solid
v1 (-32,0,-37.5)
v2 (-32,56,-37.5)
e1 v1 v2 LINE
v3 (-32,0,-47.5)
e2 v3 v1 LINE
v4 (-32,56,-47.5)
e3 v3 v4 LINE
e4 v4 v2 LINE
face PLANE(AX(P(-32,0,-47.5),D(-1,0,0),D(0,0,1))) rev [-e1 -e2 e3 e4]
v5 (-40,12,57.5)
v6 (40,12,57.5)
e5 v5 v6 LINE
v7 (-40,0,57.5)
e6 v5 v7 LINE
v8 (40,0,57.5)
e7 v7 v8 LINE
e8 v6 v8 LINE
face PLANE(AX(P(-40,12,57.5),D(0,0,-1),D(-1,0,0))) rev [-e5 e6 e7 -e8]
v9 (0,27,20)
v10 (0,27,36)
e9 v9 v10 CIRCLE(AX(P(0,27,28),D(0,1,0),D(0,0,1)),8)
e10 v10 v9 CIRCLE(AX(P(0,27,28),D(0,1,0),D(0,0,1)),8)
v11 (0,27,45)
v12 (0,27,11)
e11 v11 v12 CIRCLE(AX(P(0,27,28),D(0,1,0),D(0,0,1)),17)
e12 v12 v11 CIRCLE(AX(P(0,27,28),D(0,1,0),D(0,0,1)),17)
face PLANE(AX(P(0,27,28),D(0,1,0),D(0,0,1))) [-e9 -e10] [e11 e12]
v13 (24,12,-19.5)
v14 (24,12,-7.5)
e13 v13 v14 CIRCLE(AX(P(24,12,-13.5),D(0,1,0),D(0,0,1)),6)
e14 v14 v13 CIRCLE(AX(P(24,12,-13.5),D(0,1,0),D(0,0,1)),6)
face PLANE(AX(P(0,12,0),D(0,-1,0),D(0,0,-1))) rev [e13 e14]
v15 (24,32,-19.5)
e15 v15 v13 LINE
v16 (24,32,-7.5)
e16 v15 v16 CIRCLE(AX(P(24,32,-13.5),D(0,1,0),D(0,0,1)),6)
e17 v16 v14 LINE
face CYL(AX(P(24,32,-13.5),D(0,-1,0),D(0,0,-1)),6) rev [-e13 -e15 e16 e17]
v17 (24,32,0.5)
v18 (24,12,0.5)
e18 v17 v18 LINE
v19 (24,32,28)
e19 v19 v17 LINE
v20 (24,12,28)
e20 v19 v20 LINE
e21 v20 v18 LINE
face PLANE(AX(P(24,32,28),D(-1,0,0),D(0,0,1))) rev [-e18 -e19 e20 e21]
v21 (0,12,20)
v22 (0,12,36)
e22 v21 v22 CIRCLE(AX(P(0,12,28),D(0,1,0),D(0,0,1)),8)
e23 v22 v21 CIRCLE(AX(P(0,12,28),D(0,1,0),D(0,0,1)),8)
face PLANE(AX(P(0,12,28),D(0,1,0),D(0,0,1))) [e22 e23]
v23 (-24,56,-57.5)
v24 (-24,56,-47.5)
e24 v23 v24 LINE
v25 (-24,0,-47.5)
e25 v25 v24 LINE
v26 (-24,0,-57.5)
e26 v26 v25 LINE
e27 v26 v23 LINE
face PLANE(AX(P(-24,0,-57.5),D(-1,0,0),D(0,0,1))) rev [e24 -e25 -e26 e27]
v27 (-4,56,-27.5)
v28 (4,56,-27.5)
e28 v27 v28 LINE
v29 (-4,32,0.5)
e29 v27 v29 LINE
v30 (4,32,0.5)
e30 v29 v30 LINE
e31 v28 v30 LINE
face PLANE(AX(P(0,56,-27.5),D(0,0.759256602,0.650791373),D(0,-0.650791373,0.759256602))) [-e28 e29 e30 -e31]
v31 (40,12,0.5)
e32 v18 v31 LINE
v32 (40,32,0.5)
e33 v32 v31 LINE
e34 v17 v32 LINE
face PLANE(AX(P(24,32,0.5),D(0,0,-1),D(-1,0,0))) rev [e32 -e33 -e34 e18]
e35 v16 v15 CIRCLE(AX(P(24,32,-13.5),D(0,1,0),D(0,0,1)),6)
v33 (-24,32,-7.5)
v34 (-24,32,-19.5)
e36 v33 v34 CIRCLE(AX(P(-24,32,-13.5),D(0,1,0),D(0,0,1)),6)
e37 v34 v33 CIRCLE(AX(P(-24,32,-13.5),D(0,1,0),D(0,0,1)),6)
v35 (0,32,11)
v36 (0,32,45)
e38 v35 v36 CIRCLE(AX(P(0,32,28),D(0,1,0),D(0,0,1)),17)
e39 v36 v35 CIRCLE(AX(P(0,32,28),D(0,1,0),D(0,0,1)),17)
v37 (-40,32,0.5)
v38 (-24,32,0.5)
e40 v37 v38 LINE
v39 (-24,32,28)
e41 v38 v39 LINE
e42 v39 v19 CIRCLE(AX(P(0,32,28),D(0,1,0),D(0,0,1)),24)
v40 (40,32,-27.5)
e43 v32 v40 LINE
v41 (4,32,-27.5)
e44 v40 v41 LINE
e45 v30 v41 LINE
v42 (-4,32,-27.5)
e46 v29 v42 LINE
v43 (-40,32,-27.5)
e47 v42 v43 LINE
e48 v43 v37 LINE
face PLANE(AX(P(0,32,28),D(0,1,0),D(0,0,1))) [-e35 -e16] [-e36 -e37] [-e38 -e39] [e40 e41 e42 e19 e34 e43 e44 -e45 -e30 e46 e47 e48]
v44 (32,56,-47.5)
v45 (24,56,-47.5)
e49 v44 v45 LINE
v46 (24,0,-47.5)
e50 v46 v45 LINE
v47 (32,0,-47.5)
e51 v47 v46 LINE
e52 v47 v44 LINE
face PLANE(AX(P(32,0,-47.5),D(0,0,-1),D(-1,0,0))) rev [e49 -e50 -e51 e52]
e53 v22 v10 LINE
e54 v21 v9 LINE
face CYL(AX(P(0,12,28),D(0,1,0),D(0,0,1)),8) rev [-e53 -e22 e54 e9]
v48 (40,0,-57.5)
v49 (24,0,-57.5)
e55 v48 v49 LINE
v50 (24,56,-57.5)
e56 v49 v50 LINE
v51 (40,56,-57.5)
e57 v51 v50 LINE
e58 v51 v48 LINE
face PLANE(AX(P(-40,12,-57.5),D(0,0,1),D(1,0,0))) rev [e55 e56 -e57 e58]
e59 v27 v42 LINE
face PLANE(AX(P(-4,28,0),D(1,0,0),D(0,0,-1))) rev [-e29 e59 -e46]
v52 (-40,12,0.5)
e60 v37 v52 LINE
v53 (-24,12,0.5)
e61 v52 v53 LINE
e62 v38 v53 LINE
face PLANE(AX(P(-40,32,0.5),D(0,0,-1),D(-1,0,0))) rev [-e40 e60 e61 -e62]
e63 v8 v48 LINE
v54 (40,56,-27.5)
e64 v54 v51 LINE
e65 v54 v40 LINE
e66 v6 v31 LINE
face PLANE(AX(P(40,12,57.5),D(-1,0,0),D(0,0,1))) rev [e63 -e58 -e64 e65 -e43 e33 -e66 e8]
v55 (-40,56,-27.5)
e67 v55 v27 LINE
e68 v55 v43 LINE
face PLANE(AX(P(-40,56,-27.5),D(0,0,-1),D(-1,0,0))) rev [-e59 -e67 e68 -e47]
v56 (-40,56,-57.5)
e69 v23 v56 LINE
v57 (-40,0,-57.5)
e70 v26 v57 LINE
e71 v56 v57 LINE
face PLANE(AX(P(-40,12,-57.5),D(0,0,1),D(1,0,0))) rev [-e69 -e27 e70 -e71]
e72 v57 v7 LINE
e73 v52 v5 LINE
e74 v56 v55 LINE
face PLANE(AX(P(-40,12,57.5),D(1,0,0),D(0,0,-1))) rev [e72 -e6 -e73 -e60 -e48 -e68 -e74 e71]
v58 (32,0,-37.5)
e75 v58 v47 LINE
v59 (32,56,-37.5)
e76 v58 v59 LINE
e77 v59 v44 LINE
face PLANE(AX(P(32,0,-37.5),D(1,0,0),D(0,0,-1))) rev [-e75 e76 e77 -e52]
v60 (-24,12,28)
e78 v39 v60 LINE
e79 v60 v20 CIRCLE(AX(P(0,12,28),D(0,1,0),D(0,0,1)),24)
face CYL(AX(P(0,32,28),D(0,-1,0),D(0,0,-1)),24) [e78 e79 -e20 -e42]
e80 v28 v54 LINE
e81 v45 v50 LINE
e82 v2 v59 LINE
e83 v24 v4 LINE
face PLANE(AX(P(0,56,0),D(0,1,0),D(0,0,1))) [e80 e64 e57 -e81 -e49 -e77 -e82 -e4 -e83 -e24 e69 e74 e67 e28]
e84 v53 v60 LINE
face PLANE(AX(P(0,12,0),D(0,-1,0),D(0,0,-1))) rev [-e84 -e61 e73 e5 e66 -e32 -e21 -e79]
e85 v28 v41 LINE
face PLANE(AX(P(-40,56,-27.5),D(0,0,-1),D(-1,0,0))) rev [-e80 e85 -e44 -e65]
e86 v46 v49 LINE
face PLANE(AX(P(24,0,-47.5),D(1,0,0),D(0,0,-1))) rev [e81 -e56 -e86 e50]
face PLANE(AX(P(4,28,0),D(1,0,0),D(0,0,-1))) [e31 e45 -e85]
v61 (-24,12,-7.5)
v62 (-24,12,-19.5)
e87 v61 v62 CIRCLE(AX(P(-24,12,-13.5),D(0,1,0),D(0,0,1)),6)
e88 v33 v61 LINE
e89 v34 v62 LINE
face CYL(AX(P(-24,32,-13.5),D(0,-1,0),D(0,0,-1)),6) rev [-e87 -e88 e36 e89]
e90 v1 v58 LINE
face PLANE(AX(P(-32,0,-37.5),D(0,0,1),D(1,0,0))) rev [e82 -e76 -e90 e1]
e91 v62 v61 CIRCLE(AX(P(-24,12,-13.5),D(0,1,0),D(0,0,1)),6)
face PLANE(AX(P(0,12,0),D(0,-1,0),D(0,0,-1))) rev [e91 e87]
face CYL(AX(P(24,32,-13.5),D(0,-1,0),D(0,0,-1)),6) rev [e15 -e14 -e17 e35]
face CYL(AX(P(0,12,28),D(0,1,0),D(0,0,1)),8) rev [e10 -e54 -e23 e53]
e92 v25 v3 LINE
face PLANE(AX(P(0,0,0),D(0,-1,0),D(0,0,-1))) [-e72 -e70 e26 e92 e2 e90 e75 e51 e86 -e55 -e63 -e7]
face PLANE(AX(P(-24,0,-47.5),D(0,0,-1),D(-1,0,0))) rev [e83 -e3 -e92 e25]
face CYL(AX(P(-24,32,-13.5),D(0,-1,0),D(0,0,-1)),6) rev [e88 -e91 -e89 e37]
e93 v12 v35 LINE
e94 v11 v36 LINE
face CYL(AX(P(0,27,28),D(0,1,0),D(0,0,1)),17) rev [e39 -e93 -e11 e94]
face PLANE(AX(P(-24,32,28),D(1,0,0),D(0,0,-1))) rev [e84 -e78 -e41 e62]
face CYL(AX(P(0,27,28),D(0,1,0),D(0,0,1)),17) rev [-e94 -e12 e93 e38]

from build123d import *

# Parameters (mm, degrees)
BASE_PLATE_SKETCH_W    = 80
BASE_PLATE_SKETCH_H    = 115
BASE_PLATE_DEPTH       = 12
BACK_WALL_SKETCH_W     = 80
BACK_WALL_SKETCH_H     = 30
BACK_WALL_DEPTH        = 44
WALL_SLOT_CUT_DEPTH    = 90.678592763
BOSS_PAD_SKETCH_R      = 6
BOSS_PAD_DEPTH         = 20
COUNTERBORE_SKETCH_R   = 17
COUNTERBORE_34X5_DEPTH = 5
BORE_SKETCH_R          = 8
BORE_16_DEPTH          = 15
SUPPORT_RIB_8MM_REACH  = 91.679
RIB_SKETCH_WALL_W      = 218.235363356
RIB_SKETCH_WALL_H      = 8


with BuildPart() as part:
    # Base Plate Sketch → Base Plate (new body)
    with BuildSketch(Plane(origin=(0, 0, 0), x_dir=(1, 0, 0), z_dir=(0, 1, 0))):
        Rectangle(BASE_PLATE_SKETCH_W, BASE_PLATE_SKETCH_H)
    extrude(amount=BASE_PLATE_DEPTH)

    # Back Wall Sketch → Back Wall (add)
    with BuildSketch(Plane(origin=(0, 12, 0), x_dir=(1, 0, 0), z_dir=(0, 1, 0))):
        with Locations((0, 42.5)):
            Rectangle(BACK_WALL_SKETCH_W, BACK_WALL_SKETCH_H)
    extrude(amount=BACK_WALL_DEPTH)

    # Wall Slot Sketch → Wall Slot Cut (cut, through all)
    with BuildSketch(Plane(origin=(0, 56, 0), x_dir=(1, 0, 0), z_dir=(0, 1, 0))):
        Polygon((-24, 57.5), (-24, 47.5), (-32, 47.5), (-32, 37.5), (32, 37.5), (32, 47.5), (24, 47.5), (24, 57.5), align=None)
    extrude(amount=-WALL_SLOT_CUT_DEPTH, mode=Mode.SUBTRACT)

    # Boss Pad Sketch → Boss Pad (add)
    with BuildSketch(Plane(origin=(0, 12, 0), x_dir=(1, 0, 0), z_dir=(0, 1, 0))):
        with BuildLine():
            Line((-40, 27.5), (40, 27.5))
            Line((40, 27.5), (40, -0.5))
            Line((40, -0.5), (24, -0.5))
            Line((24, -0.5), (24, -28))
            ThreePointArc((24, -28), (0, -52), (-24, -28))
            Line((-24, -28), (-24, -0.5))
            Line((-24, -0.5), (-40, -0.5))
            Line((-40, -0.5), (-40, 27.5))
        make_face()
        with Locations(Location((-24, 13.5, 0), (0, 0, 270))):
            Circle(BOSS_PAD_SKETCH_R, mode=Mode.SUBTRACT)
        with Locations(Location((24, 13.5, 0), (0, 0, 270))):
            Circle(BOSS_PAD_SKETCH_R, mode=Mode.SUBTRACT)
    extrude(amount=BOSS_PAD_DEPTH)

    # Counterbore Sketch → Counterbore Ø34x5 (cut)
    with BuildSketch(Plane(origin=(0, 32, 0), x_dir=(1, 0, 0), z_dir=(0, 1, 0))):
        with Locations(Location((0, -28, 0), (0, 0, 270))):
            Circle(COUNTERBORE_SKETCH_R)
    extrude(amount=-COUNTERBORE_34X5_DEPTH, mode=Mode.SUBTRACT)

    # Bore Sketch → Bore Ø16 (cut)
    with BuildSketch(Plane(origin=(0, 27, 0), x_dir=(1, 0, 0), z_dir=(0, 1, 0))):
        with Locations(Location((0, -28, 0), (0, 0, 270))):
            Circle(BORE_SKETCH_R)
    extrude(amount=-BORE_16_DEPTH, mode=Mode.SUBTRACT)

    # Rib Sketch wall → Support Rib 8mm (add, up to next)
    with BuildSketch(Plane(origin=(0, 44, -13.5), x_dir=(0, -0.650791373456, 0.759256602365), z_dir=(0, -0.759256602365, -0.650791373456)), mode=Mode.PRIVATE) as support_rib_8mm_sk1:
        Rectangle(RIB_SKETCH_WALL_W, RIB_SKETCH_WALL_H)
    support_rib_8mm_tool1 = extrude(support_rib_8mm_sk1.sketch, amount=SUPPORT_RIB_8MM_REACH, mode=Mode.PRIVATE) - part.part
    add(support_rib_8mm_tool1.solids().sort_by_distance((0, 44, -13.5))[0])


solid = part.part
